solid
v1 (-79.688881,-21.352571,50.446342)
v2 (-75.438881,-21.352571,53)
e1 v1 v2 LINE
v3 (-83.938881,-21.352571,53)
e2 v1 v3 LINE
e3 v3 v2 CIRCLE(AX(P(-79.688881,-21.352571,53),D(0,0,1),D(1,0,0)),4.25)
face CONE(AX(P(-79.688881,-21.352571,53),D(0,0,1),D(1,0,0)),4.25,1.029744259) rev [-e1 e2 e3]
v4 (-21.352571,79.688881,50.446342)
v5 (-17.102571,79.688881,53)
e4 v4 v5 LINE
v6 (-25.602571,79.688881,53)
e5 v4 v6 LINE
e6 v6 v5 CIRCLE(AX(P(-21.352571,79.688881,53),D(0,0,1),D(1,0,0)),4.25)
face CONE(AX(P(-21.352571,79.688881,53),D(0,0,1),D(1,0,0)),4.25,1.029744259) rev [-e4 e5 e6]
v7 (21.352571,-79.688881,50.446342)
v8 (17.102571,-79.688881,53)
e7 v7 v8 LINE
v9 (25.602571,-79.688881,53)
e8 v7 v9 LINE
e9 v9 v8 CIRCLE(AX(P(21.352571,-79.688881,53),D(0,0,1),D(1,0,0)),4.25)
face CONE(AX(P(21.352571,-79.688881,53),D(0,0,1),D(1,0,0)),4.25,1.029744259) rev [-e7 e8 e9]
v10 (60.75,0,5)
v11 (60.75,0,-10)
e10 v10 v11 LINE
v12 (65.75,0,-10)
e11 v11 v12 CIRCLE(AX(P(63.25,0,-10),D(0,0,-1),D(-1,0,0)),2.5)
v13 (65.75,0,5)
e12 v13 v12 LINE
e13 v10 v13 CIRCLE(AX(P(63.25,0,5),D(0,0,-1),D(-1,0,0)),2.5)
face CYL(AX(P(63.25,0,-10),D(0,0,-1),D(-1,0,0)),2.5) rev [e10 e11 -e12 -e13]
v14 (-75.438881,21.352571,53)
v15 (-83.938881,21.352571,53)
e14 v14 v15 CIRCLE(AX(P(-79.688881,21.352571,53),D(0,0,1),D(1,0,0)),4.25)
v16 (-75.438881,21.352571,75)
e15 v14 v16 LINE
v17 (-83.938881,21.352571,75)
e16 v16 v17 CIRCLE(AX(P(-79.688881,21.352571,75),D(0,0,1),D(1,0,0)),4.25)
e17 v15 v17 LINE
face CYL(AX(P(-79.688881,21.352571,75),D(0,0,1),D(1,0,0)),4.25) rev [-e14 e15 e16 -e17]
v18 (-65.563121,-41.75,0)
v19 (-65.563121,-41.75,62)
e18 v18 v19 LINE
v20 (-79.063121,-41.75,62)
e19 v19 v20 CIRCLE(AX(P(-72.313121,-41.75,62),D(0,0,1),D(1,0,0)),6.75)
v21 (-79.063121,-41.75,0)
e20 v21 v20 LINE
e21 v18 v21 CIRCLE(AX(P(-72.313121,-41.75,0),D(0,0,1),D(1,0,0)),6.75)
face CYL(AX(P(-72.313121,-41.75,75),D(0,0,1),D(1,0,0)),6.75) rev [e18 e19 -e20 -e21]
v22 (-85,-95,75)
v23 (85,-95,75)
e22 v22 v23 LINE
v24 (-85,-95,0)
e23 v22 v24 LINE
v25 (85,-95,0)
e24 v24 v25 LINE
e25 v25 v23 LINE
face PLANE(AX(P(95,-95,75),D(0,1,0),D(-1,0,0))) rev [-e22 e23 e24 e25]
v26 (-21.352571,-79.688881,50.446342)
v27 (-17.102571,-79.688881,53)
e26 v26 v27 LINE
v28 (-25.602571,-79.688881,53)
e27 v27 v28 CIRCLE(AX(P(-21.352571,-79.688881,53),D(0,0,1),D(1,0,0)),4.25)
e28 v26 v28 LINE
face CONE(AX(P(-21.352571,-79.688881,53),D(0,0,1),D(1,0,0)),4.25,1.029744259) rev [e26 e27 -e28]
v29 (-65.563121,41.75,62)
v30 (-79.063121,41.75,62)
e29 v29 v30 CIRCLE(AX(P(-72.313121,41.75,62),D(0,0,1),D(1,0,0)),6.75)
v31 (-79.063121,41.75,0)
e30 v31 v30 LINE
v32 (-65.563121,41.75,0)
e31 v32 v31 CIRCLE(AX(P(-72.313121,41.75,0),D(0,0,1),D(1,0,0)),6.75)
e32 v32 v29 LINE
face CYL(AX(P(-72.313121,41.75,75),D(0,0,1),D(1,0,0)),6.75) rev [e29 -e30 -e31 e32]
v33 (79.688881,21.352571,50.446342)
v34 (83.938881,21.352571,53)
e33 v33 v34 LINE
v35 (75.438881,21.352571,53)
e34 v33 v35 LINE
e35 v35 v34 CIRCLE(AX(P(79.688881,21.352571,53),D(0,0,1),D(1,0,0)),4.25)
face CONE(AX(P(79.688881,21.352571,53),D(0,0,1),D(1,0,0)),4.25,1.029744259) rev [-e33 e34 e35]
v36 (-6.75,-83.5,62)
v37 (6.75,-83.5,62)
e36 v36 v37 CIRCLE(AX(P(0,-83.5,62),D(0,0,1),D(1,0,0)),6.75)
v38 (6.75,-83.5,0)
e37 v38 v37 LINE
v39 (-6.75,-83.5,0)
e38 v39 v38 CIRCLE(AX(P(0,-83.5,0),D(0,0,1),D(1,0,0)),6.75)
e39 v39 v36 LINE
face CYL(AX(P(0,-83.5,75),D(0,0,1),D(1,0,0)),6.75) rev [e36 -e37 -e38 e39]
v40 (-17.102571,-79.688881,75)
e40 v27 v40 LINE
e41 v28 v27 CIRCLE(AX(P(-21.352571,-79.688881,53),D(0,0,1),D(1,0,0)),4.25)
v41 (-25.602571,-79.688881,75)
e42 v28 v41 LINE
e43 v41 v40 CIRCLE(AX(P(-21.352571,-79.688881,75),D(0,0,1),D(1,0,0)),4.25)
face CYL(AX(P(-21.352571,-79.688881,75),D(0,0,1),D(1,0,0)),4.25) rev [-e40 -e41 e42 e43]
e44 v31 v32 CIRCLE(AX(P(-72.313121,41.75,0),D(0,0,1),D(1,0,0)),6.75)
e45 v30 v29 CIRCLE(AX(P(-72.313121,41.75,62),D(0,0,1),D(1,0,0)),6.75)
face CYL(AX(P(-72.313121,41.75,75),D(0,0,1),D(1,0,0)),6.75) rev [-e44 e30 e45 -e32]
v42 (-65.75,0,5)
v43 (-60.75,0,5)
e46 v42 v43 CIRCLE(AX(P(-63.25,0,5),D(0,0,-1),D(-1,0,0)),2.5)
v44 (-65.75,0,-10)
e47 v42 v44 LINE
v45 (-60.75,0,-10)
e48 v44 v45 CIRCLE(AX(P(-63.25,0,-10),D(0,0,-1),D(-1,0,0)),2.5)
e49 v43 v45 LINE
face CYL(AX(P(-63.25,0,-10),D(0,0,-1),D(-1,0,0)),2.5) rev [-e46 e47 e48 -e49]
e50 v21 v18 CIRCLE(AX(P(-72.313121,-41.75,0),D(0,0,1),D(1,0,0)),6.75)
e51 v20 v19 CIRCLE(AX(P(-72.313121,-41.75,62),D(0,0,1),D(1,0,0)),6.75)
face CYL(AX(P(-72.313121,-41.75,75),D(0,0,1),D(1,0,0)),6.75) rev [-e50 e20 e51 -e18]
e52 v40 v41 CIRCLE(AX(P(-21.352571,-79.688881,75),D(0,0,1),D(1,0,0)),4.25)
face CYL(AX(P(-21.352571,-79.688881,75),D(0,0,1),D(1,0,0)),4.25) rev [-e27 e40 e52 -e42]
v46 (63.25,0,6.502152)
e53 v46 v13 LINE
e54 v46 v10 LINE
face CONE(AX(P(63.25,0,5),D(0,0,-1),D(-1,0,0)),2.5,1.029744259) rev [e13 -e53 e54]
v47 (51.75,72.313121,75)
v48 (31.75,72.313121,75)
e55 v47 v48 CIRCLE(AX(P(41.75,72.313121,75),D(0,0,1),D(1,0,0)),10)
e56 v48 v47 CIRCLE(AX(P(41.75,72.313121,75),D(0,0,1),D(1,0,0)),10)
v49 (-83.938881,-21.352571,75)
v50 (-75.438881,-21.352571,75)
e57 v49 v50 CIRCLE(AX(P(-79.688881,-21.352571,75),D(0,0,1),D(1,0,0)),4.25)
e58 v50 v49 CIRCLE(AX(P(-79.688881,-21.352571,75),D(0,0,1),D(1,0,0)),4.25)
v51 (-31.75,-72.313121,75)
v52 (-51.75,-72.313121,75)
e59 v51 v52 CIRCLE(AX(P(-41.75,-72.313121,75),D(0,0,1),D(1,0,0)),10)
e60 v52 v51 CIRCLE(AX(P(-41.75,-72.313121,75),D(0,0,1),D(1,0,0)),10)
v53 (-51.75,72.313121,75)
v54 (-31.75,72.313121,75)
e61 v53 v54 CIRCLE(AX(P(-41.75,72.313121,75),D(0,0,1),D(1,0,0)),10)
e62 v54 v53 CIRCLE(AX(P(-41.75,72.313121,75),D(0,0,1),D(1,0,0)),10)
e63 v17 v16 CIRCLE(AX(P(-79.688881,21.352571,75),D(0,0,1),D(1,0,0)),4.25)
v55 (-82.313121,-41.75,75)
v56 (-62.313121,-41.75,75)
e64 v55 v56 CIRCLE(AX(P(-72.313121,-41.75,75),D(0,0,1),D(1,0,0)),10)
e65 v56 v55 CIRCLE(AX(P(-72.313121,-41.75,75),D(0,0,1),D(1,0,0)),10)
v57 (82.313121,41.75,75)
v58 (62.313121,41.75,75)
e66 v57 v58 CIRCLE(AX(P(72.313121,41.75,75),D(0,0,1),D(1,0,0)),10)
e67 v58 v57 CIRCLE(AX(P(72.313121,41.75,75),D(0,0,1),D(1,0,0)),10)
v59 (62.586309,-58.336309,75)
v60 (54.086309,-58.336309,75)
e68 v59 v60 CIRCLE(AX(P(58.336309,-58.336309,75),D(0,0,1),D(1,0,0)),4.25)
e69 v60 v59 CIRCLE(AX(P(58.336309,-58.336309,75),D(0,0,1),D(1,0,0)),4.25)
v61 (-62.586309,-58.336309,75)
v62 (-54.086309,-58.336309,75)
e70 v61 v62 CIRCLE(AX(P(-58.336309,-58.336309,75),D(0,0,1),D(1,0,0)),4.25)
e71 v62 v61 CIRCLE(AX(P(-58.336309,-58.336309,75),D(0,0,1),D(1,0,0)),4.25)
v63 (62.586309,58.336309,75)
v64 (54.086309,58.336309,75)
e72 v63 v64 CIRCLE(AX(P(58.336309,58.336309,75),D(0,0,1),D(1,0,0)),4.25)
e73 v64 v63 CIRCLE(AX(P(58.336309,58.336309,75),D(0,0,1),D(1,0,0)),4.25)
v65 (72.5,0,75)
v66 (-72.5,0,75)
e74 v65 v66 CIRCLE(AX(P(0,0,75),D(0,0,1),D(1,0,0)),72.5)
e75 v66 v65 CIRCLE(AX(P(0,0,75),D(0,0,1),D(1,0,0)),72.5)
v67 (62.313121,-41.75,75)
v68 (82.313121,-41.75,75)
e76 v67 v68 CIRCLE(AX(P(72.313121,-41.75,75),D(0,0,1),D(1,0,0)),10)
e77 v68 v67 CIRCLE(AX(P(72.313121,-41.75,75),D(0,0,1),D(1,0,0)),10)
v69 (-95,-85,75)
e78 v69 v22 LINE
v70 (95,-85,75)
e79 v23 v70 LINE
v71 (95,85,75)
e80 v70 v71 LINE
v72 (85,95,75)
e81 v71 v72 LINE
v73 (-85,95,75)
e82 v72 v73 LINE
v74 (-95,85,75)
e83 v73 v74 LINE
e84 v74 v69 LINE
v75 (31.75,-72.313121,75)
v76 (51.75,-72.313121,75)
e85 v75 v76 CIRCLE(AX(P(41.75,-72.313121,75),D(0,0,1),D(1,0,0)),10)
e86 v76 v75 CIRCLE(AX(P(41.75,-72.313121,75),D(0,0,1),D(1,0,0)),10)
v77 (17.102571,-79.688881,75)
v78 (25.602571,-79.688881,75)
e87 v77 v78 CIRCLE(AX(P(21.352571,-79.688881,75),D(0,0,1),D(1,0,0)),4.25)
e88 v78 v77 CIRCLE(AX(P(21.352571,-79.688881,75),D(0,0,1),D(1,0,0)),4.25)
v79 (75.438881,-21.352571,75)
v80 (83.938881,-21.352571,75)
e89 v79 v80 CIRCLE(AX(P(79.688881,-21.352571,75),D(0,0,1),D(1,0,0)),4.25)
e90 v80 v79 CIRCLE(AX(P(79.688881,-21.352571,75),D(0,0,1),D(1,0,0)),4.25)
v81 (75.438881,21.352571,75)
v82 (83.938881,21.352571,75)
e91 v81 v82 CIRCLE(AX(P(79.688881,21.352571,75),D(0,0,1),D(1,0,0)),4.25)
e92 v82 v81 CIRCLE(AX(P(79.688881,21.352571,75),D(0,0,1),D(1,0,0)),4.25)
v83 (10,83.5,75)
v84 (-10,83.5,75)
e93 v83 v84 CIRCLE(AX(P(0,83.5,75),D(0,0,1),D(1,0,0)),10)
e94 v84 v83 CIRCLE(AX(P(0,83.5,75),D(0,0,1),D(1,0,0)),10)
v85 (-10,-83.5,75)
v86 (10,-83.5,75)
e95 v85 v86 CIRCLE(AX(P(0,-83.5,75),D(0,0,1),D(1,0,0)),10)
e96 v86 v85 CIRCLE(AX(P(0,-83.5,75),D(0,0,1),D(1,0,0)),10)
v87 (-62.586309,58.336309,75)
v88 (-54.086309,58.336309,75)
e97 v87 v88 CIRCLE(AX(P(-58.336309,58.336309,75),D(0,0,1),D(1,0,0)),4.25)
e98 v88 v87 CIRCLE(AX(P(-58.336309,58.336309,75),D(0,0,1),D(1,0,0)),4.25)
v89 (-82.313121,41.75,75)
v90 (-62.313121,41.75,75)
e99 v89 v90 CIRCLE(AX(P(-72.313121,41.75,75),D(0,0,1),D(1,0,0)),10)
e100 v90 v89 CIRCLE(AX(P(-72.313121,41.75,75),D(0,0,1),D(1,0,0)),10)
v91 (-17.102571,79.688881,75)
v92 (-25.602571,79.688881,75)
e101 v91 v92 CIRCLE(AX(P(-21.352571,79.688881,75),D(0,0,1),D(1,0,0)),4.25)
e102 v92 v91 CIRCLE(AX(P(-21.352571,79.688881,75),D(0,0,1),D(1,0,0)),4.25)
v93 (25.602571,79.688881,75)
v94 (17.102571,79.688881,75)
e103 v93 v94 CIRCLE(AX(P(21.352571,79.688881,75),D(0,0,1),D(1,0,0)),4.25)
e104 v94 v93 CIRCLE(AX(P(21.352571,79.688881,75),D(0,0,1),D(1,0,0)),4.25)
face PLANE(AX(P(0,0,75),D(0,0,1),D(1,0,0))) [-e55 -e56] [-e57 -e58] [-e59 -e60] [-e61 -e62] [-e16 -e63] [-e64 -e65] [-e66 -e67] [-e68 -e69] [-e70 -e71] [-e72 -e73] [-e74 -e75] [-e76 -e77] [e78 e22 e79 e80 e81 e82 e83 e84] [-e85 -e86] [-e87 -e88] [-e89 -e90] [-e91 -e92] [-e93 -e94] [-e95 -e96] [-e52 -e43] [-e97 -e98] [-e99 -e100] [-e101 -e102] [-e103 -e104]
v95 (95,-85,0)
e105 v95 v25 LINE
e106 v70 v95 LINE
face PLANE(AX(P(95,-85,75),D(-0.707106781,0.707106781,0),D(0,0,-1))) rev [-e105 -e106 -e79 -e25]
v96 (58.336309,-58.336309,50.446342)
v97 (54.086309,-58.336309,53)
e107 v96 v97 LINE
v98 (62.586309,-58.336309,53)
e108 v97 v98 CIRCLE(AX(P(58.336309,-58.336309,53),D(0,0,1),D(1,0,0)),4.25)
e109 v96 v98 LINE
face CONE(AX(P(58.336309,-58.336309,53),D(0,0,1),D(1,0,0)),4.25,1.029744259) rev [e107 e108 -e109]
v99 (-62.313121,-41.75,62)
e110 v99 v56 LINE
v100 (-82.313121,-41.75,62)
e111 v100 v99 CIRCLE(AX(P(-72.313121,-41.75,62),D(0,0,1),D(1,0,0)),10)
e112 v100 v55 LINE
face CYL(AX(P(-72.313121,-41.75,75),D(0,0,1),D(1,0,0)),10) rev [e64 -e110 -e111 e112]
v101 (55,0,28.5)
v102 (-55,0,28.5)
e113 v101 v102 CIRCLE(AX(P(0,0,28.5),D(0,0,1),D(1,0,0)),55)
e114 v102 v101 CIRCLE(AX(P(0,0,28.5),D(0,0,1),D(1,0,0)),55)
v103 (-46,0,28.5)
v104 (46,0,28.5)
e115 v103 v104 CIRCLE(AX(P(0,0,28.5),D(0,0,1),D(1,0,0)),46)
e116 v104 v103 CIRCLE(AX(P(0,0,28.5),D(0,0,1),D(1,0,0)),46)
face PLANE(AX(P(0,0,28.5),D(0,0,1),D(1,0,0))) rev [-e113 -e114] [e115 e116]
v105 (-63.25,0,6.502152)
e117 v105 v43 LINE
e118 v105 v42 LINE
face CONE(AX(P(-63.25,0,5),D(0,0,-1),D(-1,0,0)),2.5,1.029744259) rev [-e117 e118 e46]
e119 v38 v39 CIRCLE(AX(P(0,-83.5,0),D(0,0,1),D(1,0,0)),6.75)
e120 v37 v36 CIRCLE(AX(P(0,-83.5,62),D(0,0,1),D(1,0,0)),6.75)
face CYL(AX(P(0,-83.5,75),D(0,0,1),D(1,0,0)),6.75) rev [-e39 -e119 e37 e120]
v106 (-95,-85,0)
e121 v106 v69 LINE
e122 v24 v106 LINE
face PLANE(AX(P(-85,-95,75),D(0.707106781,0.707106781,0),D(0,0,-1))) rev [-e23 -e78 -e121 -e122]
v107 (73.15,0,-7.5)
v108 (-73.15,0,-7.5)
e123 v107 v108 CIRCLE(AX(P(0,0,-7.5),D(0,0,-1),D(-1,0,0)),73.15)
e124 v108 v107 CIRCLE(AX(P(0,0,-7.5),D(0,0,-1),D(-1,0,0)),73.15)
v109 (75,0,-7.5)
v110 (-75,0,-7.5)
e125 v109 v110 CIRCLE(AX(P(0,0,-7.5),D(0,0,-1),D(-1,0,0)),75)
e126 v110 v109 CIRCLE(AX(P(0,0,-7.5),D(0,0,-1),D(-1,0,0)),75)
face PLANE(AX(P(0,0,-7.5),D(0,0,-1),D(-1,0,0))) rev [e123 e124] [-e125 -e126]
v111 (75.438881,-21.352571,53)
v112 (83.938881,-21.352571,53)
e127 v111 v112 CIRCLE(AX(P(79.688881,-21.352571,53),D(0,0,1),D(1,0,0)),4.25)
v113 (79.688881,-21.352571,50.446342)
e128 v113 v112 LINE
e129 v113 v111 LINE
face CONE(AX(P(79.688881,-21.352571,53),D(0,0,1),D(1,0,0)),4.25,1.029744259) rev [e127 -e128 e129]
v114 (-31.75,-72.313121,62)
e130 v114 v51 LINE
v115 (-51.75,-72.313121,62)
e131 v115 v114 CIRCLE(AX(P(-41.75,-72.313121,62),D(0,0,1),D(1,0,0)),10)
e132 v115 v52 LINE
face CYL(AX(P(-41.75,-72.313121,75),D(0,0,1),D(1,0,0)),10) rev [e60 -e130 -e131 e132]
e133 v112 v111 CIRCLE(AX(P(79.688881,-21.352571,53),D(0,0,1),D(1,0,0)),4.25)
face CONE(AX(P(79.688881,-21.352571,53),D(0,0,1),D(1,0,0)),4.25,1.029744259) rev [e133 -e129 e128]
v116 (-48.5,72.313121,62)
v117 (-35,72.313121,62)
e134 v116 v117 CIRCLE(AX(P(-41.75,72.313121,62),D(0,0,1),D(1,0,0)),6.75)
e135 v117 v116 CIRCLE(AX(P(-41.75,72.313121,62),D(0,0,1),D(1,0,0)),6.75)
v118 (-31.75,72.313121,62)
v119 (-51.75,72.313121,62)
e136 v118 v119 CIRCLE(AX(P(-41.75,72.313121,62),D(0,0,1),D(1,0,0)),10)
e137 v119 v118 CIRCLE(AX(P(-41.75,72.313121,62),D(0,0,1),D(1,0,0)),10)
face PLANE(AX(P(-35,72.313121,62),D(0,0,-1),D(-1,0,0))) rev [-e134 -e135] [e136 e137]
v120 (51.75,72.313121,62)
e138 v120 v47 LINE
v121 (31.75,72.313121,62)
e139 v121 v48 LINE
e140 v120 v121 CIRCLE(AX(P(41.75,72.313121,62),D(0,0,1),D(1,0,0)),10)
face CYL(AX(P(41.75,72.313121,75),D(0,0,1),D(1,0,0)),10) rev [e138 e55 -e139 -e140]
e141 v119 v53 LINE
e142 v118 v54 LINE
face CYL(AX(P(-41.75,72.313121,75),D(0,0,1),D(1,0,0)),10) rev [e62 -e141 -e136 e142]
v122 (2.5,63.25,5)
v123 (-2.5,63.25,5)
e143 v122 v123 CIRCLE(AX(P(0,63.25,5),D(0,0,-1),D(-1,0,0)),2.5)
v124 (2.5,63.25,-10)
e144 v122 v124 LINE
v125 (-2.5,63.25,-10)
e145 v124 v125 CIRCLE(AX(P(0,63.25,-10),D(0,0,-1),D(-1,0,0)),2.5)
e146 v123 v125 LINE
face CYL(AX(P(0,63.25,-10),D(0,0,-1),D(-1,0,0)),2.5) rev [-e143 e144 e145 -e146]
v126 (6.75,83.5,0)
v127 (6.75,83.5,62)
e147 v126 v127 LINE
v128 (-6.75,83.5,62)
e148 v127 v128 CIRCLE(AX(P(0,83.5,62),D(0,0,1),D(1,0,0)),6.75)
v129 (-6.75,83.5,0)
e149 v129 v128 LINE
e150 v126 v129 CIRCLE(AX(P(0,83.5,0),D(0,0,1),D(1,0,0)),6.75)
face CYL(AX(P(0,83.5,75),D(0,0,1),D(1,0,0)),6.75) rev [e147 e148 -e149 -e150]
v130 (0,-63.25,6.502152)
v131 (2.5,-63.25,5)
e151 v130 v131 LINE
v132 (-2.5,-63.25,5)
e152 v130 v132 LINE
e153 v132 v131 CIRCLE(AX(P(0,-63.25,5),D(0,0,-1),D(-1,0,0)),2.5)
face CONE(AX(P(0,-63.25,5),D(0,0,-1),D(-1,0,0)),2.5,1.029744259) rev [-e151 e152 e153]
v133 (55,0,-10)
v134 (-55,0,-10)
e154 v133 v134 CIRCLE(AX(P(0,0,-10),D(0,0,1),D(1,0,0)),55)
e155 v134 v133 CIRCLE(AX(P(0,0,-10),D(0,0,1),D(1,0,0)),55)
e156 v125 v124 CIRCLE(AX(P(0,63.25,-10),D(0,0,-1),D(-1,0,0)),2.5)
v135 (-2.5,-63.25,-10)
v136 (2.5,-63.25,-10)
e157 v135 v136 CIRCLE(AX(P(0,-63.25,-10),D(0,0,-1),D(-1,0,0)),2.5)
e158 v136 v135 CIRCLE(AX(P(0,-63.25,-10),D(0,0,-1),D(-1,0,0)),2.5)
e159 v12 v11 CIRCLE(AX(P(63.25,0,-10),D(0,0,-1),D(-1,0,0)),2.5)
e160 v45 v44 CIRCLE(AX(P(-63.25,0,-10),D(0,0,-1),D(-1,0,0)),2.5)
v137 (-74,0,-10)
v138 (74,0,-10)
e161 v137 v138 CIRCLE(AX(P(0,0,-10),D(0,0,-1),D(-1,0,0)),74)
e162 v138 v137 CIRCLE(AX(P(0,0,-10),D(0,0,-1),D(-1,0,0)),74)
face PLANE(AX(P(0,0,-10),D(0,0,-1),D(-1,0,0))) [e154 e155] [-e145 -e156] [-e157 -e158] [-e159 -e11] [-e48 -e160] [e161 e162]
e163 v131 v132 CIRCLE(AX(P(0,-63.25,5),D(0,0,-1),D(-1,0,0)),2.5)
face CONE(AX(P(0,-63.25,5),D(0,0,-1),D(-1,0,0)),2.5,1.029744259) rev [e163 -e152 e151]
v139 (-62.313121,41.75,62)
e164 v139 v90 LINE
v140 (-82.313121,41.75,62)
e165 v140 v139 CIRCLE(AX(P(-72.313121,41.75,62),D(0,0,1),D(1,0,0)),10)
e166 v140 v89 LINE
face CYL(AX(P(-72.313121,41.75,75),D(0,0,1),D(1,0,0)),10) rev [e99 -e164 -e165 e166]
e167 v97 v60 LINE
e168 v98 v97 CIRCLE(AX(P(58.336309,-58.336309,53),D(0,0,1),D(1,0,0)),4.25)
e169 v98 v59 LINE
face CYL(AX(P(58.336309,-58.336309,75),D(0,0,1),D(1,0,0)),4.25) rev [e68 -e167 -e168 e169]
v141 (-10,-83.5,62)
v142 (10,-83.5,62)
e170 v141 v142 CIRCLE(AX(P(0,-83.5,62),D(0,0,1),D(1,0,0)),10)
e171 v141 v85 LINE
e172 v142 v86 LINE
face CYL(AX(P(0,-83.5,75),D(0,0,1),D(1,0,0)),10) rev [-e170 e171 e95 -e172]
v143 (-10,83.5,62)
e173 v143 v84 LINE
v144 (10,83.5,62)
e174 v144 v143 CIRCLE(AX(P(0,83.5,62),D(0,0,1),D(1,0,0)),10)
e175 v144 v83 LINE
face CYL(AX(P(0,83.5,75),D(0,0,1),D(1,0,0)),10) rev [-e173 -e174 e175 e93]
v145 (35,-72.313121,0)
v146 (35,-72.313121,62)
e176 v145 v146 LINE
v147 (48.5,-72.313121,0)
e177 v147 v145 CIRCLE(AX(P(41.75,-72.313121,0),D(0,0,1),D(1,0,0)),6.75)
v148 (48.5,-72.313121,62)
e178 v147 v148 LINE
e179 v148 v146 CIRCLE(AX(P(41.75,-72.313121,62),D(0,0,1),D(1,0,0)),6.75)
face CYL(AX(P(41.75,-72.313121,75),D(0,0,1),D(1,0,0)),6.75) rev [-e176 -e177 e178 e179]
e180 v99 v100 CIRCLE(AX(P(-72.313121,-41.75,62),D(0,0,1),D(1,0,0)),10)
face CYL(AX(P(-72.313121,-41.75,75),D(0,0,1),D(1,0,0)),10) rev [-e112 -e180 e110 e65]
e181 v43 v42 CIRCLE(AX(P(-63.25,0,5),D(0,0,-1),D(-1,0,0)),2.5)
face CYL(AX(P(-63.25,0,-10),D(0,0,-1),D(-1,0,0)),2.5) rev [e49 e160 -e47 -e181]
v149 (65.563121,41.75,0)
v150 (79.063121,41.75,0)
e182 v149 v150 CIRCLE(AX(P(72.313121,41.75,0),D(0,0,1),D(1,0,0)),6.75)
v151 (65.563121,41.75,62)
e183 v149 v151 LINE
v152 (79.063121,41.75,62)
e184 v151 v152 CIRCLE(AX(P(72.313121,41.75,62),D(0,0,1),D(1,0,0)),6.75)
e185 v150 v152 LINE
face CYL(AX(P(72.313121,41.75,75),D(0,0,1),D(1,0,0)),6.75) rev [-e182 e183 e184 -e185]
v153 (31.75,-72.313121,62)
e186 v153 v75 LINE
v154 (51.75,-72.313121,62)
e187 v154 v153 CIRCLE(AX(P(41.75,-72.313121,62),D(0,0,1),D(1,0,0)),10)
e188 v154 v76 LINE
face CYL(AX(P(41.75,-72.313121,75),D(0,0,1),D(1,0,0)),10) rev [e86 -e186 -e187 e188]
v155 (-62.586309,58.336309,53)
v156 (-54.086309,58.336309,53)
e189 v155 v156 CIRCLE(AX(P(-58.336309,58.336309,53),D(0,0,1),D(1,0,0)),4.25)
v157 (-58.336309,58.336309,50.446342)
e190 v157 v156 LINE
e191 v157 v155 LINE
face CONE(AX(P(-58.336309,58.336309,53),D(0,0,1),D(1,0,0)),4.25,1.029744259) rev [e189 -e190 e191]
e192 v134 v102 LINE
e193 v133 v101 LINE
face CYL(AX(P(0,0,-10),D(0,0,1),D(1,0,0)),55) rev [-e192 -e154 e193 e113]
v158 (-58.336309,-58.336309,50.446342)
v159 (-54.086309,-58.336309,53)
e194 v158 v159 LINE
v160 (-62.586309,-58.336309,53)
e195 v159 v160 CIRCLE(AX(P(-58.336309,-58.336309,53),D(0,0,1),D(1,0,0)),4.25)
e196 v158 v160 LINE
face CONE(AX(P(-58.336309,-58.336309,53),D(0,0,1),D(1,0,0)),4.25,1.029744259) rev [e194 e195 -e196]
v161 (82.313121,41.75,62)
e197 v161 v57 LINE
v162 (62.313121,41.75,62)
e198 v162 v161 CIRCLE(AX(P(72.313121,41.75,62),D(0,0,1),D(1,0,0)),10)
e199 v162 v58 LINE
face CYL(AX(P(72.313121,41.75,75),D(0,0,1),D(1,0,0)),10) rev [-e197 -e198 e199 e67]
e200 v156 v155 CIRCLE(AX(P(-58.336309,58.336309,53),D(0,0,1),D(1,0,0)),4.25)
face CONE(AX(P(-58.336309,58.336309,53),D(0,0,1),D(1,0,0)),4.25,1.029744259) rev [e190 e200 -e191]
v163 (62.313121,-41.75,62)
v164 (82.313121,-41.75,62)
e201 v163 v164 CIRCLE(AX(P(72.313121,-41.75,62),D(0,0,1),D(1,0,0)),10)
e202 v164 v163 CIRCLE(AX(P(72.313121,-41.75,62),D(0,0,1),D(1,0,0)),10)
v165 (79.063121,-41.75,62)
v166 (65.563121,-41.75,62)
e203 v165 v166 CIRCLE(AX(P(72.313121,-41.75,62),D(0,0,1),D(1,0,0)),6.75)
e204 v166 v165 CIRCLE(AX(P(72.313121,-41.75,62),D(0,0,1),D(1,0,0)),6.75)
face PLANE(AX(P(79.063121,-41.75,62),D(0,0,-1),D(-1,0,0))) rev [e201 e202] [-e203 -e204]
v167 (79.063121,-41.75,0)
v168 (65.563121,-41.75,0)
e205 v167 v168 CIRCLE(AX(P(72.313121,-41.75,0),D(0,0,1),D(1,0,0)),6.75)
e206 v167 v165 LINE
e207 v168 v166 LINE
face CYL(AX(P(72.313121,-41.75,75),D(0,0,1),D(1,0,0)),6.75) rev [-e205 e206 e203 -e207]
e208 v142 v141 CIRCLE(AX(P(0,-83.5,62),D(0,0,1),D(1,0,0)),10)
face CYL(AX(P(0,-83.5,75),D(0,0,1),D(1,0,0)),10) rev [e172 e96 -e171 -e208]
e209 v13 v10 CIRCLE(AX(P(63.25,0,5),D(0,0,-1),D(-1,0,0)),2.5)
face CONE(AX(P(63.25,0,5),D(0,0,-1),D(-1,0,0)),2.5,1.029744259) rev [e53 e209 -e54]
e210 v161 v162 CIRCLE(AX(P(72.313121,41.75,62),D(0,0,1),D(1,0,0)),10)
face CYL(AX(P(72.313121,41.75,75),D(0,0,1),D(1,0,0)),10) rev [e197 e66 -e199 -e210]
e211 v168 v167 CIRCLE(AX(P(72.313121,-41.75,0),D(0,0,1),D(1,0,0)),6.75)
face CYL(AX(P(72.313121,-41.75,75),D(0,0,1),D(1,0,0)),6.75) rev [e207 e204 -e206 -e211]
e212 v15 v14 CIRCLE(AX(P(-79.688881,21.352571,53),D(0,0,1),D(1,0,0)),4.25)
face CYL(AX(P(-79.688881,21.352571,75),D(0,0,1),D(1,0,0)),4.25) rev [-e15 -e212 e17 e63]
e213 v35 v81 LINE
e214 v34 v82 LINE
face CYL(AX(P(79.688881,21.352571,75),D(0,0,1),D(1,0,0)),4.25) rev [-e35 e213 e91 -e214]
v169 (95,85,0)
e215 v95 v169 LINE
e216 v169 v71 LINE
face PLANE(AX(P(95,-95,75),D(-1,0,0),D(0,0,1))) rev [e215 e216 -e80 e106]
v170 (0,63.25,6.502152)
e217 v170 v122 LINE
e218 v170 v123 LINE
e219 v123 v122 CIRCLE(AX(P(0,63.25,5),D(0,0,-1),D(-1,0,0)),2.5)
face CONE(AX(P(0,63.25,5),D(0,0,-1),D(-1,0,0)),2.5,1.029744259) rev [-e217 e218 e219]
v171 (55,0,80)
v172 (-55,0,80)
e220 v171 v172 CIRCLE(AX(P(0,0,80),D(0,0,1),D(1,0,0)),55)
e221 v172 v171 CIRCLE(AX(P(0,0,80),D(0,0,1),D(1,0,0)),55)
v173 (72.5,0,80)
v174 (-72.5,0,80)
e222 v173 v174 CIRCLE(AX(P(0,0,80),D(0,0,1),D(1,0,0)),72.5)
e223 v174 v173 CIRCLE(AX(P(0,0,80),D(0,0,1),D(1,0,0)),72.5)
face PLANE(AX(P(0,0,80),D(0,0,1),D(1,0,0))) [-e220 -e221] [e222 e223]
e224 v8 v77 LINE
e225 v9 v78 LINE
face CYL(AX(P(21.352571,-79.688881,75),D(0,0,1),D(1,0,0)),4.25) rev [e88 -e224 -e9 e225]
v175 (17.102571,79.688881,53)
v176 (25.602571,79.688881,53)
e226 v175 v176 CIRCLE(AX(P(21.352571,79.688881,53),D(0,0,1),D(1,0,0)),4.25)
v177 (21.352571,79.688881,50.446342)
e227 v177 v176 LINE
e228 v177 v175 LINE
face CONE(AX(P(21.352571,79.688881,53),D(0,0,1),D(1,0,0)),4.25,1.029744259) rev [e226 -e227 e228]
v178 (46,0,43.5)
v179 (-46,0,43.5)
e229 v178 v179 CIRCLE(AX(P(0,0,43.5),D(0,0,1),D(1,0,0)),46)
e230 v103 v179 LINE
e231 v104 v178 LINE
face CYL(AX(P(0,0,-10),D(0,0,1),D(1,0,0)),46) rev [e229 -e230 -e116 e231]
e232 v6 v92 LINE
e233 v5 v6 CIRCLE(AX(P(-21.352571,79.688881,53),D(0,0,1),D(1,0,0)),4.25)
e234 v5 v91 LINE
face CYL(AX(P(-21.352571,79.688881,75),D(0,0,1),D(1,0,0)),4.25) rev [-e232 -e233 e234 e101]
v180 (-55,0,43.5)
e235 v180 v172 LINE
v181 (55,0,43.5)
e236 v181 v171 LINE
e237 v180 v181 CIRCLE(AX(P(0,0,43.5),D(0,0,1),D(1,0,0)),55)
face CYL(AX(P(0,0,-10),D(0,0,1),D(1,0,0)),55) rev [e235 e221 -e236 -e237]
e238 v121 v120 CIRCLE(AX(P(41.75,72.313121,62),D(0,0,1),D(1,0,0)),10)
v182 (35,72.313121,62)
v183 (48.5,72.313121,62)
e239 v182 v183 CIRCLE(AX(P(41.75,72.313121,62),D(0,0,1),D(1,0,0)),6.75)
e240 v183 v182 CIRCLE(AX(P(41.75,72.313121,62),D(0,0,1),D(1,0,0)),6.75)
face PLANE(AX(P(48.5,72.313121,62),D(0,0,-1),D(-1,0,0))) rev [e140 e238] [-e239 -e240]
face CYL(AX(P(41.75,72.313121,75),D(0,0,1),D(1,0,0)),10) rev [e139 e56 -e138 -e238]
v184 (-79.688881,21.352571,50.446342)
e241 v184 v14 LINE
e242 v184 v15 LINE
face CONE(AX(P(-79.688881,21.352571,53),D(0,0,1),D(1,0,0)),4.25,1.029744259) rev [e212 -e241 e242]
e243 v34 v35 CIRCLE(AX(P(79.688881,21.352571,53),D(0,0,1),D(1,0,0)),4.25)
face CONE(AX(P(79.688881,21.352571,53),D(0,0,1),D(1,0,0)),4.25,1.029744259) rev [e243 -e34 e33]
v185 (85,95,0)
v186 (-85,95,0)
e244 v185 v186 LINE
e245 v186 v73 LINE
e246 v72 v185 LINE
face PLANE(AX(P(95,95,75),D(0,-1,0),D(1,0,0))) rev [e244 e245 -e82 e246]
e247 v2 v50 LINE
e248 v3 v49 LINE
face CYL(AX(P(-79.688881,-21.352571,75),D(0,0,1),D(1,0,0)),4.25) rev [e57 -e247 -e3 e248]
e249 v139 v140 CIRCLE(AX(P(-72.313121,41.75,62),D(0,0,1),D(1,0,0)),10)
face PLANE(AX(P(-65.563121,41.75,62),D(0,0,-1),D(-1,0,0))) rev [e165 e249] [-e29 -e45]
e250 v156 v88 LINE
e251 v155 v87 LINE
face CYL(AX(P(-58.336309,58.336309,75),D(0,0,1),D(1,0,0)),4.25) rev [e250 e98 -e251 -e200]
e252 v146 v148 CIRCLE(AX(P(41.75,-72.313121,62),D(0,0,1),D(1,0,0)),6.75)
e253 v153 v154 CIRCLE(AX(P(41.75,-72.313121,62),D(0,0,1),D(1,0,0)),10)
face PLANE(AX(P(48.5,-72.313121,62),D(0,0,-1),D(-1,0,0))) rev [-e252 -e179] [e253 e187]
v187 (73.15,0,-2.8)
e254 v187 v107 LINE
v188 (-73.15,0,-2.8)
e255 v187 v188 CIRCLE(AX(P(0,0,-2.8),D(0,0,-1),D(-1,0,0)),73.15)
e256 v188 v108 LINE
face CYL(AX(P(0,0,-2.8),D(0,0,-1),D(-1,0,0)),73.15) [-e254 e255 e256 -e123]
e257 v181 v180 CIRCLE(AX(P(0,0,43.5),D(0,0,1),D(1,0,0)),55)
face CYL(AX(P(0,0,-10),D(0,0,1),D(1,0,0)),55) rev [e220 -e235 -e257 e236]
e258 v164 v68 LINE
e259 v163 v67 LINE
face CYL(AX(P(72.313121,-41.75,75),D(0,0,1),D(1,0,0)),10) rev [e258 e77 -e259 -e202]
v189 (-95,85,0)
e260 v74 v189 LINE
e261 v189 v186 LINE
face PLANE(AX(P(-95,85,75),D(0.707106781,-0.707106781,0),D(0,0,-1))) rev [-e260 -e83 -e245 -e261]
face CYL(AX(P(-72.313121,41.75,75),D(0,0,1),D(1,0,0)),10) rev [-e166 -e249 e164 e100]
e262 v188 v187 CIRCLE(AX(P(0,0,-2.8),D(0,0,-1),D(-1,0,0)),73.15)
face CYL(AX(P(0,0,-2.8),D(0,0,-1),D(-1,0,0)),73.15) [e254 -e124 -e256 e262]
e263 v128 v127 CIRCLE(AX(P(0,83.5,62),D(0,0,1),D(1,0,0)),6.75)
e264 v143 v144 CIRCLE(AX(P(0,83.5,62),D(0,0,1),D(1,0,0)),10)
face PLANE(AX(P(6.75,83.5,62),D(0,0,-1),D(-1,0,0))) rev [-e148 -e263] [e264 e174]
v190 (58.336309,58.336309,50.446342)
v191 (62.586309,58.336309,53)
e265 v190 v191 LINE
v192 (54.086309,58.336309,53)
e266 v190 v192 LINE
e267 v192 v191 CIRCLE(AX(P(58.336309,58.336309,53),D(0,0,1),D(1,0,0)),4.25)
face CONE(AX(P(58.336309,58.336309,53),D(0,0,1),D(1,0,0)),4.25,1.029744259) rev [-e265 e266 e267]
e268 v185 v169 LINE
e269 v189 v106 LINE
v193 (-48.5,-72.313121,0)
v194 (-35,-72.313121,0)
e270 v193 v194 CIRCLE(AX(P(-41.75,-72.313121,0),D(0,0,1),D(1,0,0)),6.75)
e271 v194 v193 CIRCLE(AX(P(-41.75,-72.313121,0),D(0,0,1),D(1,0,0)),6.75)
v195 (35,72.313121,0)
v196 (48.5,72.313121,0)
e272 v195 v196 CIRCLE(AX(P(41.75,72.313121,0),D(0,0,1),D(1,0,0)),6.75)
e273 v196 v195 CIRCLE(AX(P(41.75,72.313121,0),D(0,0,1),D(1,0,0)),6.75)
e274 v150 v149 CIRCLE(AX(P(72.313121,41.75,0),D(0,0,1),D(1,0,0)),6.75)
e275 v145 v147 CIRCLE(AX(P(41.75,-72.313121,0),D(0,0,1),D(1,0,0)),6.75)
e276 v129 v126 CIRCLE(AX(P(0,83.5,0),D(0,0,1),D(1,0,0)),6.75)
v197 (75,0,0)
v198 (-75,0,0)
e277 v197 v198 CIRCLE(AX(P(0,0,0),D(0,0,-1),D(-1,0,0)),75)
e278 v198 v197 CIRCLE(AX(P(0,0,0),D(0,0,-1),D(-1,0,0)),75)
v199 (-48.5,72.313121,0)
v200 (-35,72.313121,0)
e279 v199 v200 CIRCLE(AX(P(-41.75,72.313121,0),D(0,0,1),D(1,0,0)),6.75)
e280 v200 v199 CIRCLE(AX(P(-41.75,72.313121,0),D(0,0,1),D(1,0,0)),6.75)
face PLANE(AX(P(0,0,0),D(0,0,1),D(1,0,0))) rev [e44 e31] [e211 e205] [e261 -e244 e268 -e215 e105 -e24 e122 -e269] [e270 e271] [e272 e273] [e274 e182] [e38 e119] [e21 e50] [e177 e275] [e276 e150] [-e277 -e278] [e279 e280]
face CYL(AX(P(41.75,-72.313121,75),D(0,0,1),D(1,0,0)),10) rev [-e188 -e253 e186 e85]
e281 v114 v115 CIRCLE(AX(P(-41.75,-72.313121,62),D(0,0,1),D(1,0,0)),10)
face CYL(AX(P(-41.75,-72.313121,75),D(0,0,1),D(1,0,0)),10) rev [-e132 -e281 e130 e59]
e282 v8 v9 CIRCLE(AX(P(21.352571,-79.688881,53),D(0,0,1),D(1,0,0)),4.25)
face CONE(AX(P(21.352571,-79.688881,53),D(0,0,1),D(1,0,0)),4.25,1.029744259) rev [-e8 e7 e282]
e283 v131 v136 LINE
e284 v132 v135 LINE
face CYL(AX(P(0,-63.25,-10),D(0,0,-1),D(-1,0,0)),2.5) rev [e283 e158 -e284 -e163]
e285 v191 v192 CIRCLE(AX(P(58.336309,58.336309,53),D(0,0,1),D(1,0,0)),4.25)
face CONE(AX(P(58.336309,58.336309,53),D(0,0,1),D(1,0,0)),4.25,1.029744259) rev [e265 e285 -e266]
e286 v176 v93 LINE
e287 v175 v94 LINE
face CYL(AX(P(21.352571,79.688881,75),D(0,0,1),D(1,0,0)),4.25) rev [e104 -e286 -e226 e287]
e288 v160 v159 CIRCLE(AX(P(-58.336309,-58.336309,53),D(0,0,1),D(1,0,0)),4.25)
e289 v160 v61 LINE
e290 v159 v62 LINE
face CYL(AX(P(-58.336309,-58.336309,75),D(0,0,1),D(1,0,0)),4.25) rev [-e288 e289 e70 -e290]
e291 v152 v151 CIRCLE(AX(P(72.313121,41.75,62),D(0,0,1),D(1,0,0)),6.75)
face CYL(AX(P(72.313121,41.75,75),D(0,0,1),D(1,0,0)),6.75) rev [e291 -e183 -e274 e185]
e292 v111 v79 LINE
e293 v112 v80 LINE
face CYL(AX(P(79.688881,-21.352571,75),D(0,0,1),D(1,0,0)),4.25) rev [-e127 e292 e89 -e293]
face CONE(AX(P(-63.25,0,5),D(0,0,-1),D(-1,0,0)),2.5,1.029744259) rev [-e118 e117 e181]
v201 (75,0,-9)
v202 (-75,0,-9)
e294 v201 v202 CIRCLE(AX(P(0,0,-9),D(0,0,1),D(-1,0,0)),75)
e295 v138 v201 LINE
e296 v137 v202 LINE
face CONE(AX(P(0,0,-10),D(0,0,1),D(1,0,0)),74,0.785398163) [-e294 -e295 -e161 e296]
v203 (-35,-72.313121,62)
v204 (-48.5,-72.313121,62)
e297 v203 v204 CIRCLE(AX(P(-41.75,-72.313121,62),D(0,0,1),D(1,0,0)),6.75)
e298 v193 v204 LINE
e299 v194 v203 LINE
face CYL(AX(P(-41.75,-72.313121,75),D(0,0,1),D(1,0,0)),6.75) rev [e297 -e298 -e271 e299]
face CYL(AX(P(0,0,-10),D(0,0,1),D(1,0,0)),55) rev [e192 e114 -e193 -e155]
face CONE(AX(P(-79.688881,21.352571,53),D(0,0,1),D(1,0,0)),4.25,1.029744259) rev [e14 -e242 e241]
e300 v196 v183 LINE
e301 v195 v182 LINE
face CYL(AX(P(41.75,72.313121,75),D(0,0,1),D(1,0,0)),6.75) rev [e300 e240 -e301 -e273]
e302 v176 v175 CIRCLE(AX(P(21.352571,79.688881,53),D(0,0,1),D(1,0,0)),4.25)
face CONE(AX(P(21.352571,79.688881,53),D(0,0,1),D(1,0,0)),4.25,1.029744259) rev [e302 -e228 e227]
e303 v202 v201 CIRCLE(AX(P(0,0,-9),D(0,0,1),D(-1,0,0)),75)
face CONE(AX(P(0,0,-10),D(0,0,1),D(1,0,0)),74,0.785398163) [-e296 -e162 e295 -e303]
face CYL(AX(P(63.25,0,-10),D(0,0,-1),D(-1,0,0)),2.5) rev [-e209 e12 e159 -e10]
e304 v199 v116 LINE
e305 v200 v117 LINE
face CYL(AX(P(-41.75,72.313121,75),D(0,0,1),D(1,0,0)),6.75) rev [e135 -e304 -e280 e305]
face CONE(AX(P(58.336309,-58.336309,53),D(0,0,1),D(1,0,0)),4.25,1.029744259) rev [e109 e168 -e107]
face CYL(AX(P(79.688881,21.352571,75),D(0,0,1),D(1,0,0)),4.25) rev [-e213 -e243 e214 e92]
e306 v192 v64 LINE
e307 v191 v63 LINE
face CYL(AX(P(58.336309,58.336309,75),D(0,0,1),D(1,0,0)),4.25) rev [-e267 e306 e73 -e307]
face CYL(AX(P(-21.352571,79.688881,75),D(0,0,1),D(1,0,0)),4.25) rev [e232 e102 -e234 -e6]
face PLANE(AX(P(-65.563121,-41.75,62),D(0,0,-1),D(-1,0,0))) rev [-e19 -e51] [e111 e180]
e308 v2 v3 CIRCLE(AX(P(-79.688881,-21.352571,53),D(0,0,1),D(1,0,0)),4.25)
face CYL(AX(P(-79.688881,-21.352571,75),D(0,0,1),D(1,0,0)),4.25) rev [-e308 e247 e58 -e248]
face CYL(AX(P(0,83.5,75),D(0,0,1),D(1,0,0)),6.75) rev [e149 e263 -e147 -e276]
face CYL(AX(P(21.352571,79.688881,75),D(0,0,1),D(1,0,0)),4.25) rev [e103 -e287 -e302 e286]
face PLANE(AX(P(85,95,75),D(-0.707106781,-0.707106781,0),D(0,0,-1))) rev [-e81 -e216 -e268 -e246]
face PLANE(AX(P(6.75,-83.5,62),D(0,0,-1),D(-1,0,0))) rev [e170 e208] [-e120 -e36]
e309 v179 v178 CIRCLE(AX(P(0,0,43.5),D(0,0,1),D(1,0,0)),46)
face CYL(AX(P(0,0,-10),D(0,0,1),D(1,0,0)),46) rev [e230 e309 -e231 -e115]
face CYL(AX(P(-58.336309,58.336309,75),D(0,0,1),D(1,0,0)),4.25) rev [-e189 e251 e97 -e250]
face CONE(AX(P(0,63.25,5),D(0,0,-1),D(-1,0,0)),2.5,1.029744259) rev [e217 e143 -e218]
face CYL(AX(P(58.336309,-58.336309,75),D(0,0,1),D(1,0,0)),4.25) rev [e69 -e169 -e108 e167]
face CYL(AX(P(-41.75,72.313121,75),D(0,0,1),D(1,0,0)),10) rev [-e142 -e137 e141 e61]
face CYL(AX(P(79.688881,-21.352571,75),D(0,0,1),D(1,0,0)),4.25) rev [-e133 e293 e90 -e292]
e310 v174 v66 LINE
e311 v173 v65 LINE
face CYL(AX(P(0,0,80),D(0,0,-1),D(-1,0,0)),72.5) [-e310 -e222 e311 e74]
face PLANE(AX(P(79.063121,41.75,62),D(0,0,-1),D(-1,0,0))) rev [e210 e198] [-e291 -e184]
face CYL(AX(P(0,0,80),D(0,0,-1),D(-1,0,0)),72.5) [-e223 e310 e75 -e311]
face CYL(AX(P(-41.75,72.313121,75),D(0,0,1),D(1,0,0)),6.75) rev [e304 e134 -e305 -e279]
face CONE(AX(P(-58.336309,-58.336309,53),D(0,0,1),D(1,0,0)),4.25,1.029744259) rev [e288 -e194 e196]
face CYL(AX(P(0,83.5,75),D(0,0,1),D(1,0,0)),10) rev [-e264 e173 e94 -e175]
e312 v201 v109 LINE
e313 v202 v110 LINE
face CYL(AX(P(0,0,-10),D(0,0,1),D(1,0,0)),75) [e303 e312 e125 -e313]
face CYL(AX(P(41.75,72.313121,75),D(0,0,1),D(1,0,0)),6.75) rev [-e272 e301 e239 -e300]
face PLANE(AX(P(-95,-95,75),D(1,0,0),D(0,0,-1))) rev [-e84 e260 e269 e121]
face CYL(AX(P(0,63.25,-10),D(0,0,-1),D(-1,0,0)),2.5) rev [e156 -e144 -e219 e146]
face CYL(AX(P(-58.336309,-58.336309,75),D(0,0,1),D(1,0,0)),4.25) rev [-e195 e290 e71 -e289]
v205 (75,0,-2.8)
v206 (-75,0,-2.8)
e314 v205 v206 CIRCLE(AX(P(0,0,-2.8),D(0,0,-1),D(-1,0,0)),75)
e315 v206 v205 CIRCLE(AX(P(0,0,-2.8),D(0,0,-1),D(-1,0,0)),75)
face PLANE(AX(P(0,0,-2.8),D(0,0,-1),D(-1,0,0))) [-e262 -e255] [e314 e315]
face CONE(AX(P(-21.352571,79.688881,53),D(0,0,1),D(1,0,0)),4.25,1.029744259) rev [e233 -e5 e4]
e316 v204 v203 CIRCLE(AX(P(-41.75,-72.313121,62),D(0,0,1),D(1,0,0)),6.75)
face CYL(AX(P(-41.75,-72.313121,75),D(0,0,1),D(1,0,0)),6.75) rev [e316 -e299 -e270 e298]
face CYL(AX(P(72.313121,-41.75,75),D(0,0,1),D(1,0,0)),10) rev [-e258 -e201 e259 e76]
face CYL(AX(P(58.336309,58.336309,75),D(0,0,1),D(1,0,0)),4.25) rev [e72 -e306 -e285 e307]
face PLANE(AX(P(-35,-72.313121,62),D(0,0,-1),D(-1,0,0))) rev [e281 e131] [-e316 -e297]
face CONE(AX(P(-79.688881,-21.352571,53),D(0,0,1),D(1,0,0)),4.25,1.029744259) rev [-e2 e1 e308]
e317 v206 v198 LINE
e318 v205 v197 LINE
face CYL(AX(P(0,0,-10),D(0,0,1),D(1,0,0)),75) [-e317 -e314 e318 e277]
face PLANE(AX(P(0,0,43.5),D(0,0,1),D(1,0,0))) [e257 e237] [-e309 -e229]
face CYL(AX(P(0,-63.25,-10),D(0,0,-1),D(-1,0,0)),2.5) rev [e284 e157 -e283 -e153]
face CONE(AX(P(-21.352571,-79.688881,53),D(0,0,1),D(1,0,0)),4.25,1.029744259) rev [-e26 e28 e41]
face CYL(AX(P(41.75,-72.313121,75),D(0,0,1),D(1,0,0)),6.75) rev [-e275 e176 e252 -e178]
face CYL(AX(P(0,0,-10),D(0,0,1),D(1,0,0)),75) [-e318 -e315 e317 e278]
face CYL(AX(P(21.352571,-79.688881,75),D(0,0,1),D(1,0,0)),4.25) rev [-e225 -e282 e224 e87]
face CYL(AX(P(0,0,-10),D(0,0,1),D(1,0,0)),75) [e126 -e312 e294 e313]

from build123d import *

# Parameters (mm, degrees)
SKETCH1_W                                            = 190
SKETCH1_H                                            = 190
BOSS_EXTRUDE1_DEPTH                                  = 75
SKETCH2_R                                            = 33
CUT_EXTRUDE1_DEPTH                                   = 154.866825534
HOLE_SIZE_PER_SOCKET_HEAD_CAP_SCREW_TYPE_D           = 13.5
HOLE_SIZE_PER_SOCKET_HEAD_CAP_SCREW_TYPE_CBORE_D     = 20
HOLE_SIZE_PER_SOCKET_HEAD_CAP_SCREW_TYPE_CBORE_DEPTH = 13
CIRPATTERN1_COUNT                                    = 12
CHAMFER1_SIZE                                        = 10
CIRPATTERN2_COUNT                                    = 12
SKETCH14_R                                           = 40
CUT_EXTRUDE5_DEPTH                                   = 50
CUT_EXTRUDE6_START                                   = -50
SKETCH15_R                                           = 40
CUT_EXTRUDE6_DEPTH                                   = 50
SKETCH17_R                                           = 75
SKETCH17_R_2                                         = 55
BOSS_EXTRUDE3_DEPTH                                  = 10
SKETCH19_R                                           = 45
CUT_EXTRUDE8_DEPTH                                   = 25
SKETCH20_R                                           = 55
CUT_EXTRUDE9_DEPTH                                   = 159.981130956
BOSS_EXTRUDE4_START                                  = -35
SKETCH21_R                                           = 55
SKETCH21_R_2                                         = 42.5
BOSS_EXTRUDE4_DEPTH                                  = 35
CHAMFER3_SIZE                                        = 1
CIRPATTERN3_COUNT                                    = 4
CUT_EXTRUDE11_START                                  = -2.5
SKETCH24_OUTSIDE_W                                   = 248.364
SKETCH24_OUTSIDE_H                                   = 248.364
SKETCH24_OUTSIDE_R                                   = 73.15
CUT_EXTRUDE11_DEPTH                                  = 4.7
SKETCH25_R                                           = 55
CUT_EXTRUDE12_DEPTH                                  = 159.981130956
BOSS_EXTRUDE5_START                                  = -31.5
SKETCH26_R                                           = 55
SKETCH26_R_2                                         = 40
BOSS_EXTRUDE5_DEPTH                                  = 15
BOSS_EXTRUDE6_START                                  = 5
SKETCH27_R                                           = 72.5
SKETCH27_R_2                                         = 55
BOSS_EXTRUDE6_DEPTH                                  = 5
SKETCH28_R                                           = 46
CUT_EXTRUDE13_DEPTH                                  = 145.610684253


with BuildPart() as part:
    # Sketch1 → Boss-Extrude1 (new body)
    with BuildSketch(Plane.XY):
        Rectangle(SKETCH1_W, SKETCH1_H)
    extrude(amount=BOSS_EXTRUDE1_DEPTH)

    # Sketch2 → Cut-Extrude1 (cut, through all)
    with BuildSketch(Plane.XY.offset(75)):
        Circle(SKETCH2_R)
    extrude(amount=-CUT_EXTRUDE1_DEPTH, mode=Mode.SUBTRACT)

    # Hole size per socket head cap screw type1 (through all)
    with Locations(Plane.XY.offset(75)):
        with Locations((0, 83.5)):
            hole_size_per_socket_head_cap_screw_type = CounterBoreHole(HOLE_SIZE_PER_SOCKET_HEAD_CAP_SCREW_TYPE_D / 2, HOLE_SIZE_PER_SOCKET_HEAD_CAP_SCREW_TYPE_CBORE_D / 2, HOLE_SIZE_PER_SOCKET_HEAD_CAP_SCREW_TYPE_CBORE_DEPTH)

    # CirPattern1: Hole size per socket head cap screw type1 ×12 about axis, 2 skipped
    cirpattern1_axis = Axis((0, 0, 0), (0, 0, -1))
    add([hole_size_per_socket_head_cap_screw_type.rotate(cirpattern1_axis, i * 360 / CIRPATTERN1_COUNT) for i in range(1, CIRPATTERN1_COUNT) if i not in (3, 9)], mode=Mode.SUBTRACT)

    # Chamfer1
    chamfer1_edges = [part.edges().sort_by_distance(p)[0] for p in [
        (-95, 95, 37.5),
        (95, 95, 37.5),
        (95, -95, 37.5),
        (-95, -95, 37.5),
    ]]
    chamfer(chamfer1_edges, length=CHAMFER1_SIZE)

    # Sketch10 → M10 Tapped Hole1 (revolve, cut)
    with BuildSketch(Plane(origin=(21.352571221, 79.688880669, 75), x_dir=(0, -1, 0), z_dir=(1, 0, 0))):
        Polygon((0, 0), (0, 24.553657631), (4.25, 22), (4.25, 0), align=None)
    m10_tapped_hole1 = revolve(axis=Axis((21.352571221, 79.688880669, 81.35), (0, 0, -1)), mode=Mode.SUBTRACT)

    # CirPattern2: M10 Tapped Hole1 ×12 about axis
    cirpattern2_axis = Axis((0, 0, 0), (0, 0, 1))
    for i in range(1, CIRPATTERN2_COUNT):
        add(m10_tapped_hole1.rotate(cirpattern2_axis, i * 360 / CIRPATTERN2_COUNT), mode=Mode.SUBTRACT)

    # Sketch14 → Cut-Extrude5 (cut)
    with BuildSketch(Plane(origin=(0, 0, 0), x_dir=(-1, 0, 0), z_dir=(0, 0, -1))):
        Circle(SKETCH14_R)
    extrude(amount=-CUT_EXTRUDE5_DEPTH, mode=Mode.SUBTRACT)

    # Sketch15 → Cut-Extrude6 (cut)
    with BuildSketch(Plane.XY.offset(75).offset(CUT_EXTRUDE6_START)):
        with Locations(Location((0, 0, 0), (0, 0, 180))):
            Circle(SKETCH15_R)
    extrude(amount=CUT_EXTRUDE6_DEPTH, mode=Mode.SUBTRACT)

    # Sketch17 → Boss-Extrude3 (add)
    with BuildSketch(Plane(origin=(0, 0, 0), x_dir=(-1, 0, 0), z_dir=(0, 0, -1))):
        Circle(SKETCH17_R)
        Circle(SKETCH17_R_2, mode=Mode.SUBTRACT)
    extrude(amount=BOSS_EXTRUDE3_DEPTH)

    # Sketch19 → Cut-Extrude8 (cut)
    with BuildSketch(Plane.XY.offset(75)):
        Circle(SKETCH19_R)
    extrude(amount=-CUT_EXTRUDE8_DEPTH, mode=Mode.SUBTRACT)

    # Sketch20 → Cut-Extrude9 (cut, through all)
    with BuildSketch(Plane.XY.offset(75)):
        Circle(SKETCH20_R)
    extrude(amount=-CUT_EXTRUDE9_DEPTH, mode=Mode.SUBTRACT)

    # Sketch21 → Boss-Extrude4 (add)
    with BuildSketch(Plane(origin=(0, 0, -10), x_dir=(-1, 0, 0), z_dir=(0, 0, -1)).offset(BOSS_EXTRUDE4_START)):
        with Locations(Location((0, 0, 0), (0, 0, 180))):
            Circle(SKETCH21_R)
        Circle(SKETCH21_R_2, mode=Mode.SUBTRACT)
    extrude(amount=BOSS_EXTRUDE4_DEPTH)

    # Chamfer3
    chamfer3_edges = [part.edges().sort_by_distance(p)[0] for p in [
        (75, 0, -10),
    ]]
    chamfer(chamfer3_edges, length=CHAMFER3_SIZE)

    # Sketch23 → M6 Tapped Hole1 (revolve, cut)
    with BuildSketch(Plane(origin=(0, 63.25, -10), x_dir=(0, 1, 0), z_dir=(1, 0, 0))):
        Polygon((0, 0), (0, 16.502151548), (2.5, 15), (2.5, 0), align=None)
    m6_tapped_hole1 = revolve(axis=Axis((0, 63.25, -16.35), (0, 0, 1)), mode=Mode.SUBTRACT)

    # CirPattern3: M6 Tapped Hole1 ×4 about axis
    cirpattern3_axis = Axis((0, 0, 0), (0, 0, 1))
    for i in range(1, CIRPATTERN3_COUNT):
        add(m6_tapped_hole1.rotate(cirpattern3_axis, i * 360 / CIRPATTERN3_COUNT), mode=Mode.SUBTRACT)

    # Sketch24 outside → Cut-Extrude11 (cut)
    with BuildSketch(Plane(origin=(0, 0, -10), x_dir=(-1, 0, 0), z_dir=(0, 0, -1)).offset(CUT_EXTRUDE11_START)):
        Rectangle(SKETCH24_OUTSIDE_W, SKETCH24_OUTSIDE_H)
        Circle(SKETCH24_OUTSIDE_R, mode=Mode.SUBTRACT)
    extrude(amount=-CUT_EXTRUDE11_DEPTH, mode=Mode.SUBTRACT)

    # Sketch25 → Cut-Extrude12 (cut, through all)
    with BuildSketch(Plane.XY.offset(75)):
        Circle(SKETCH25_R)
    extrude(amount=-CUT_EXTRUDE12_DEPTH, mode=Mode.SUBTRACT)

    # Sketch26 → Boss-Extrude5 (add)
    with BuildSketch(Plane.XY.offset(75).offset(BOSS_EXTRUDE5_START)):
        Circle(SKETCH26_R)
        Circle(SKETCH26_R_2, mode=Mode.SUBTRACT)
    extrude(amount=-BOSS_EXTRUDE5_DEPTH)

    # Sketch27 → Boss-Extrude6 (add)
    with BuildSketch(Plane.XY.offset(75).offset(BOSS_EXTRUDE6_START)):
        Circle(SKETCH27_R)
        Circle(SKETCH27_R_2, mode=Mode.SUBTRACT)
    extrude(amount=-BOSS_EXTRUDE6_DEPTH)

    # Sketch28 → Cut-Extrude13 (cut, through all)
    with BuildSketch(Plane.XY.offset(43.5)):
        Circle(SKETCH28_R)
    extrude(amount=-CUT_EXTRUDE13_DEPTH, mode=Mode.SUBTRACT)


solid = part.part
